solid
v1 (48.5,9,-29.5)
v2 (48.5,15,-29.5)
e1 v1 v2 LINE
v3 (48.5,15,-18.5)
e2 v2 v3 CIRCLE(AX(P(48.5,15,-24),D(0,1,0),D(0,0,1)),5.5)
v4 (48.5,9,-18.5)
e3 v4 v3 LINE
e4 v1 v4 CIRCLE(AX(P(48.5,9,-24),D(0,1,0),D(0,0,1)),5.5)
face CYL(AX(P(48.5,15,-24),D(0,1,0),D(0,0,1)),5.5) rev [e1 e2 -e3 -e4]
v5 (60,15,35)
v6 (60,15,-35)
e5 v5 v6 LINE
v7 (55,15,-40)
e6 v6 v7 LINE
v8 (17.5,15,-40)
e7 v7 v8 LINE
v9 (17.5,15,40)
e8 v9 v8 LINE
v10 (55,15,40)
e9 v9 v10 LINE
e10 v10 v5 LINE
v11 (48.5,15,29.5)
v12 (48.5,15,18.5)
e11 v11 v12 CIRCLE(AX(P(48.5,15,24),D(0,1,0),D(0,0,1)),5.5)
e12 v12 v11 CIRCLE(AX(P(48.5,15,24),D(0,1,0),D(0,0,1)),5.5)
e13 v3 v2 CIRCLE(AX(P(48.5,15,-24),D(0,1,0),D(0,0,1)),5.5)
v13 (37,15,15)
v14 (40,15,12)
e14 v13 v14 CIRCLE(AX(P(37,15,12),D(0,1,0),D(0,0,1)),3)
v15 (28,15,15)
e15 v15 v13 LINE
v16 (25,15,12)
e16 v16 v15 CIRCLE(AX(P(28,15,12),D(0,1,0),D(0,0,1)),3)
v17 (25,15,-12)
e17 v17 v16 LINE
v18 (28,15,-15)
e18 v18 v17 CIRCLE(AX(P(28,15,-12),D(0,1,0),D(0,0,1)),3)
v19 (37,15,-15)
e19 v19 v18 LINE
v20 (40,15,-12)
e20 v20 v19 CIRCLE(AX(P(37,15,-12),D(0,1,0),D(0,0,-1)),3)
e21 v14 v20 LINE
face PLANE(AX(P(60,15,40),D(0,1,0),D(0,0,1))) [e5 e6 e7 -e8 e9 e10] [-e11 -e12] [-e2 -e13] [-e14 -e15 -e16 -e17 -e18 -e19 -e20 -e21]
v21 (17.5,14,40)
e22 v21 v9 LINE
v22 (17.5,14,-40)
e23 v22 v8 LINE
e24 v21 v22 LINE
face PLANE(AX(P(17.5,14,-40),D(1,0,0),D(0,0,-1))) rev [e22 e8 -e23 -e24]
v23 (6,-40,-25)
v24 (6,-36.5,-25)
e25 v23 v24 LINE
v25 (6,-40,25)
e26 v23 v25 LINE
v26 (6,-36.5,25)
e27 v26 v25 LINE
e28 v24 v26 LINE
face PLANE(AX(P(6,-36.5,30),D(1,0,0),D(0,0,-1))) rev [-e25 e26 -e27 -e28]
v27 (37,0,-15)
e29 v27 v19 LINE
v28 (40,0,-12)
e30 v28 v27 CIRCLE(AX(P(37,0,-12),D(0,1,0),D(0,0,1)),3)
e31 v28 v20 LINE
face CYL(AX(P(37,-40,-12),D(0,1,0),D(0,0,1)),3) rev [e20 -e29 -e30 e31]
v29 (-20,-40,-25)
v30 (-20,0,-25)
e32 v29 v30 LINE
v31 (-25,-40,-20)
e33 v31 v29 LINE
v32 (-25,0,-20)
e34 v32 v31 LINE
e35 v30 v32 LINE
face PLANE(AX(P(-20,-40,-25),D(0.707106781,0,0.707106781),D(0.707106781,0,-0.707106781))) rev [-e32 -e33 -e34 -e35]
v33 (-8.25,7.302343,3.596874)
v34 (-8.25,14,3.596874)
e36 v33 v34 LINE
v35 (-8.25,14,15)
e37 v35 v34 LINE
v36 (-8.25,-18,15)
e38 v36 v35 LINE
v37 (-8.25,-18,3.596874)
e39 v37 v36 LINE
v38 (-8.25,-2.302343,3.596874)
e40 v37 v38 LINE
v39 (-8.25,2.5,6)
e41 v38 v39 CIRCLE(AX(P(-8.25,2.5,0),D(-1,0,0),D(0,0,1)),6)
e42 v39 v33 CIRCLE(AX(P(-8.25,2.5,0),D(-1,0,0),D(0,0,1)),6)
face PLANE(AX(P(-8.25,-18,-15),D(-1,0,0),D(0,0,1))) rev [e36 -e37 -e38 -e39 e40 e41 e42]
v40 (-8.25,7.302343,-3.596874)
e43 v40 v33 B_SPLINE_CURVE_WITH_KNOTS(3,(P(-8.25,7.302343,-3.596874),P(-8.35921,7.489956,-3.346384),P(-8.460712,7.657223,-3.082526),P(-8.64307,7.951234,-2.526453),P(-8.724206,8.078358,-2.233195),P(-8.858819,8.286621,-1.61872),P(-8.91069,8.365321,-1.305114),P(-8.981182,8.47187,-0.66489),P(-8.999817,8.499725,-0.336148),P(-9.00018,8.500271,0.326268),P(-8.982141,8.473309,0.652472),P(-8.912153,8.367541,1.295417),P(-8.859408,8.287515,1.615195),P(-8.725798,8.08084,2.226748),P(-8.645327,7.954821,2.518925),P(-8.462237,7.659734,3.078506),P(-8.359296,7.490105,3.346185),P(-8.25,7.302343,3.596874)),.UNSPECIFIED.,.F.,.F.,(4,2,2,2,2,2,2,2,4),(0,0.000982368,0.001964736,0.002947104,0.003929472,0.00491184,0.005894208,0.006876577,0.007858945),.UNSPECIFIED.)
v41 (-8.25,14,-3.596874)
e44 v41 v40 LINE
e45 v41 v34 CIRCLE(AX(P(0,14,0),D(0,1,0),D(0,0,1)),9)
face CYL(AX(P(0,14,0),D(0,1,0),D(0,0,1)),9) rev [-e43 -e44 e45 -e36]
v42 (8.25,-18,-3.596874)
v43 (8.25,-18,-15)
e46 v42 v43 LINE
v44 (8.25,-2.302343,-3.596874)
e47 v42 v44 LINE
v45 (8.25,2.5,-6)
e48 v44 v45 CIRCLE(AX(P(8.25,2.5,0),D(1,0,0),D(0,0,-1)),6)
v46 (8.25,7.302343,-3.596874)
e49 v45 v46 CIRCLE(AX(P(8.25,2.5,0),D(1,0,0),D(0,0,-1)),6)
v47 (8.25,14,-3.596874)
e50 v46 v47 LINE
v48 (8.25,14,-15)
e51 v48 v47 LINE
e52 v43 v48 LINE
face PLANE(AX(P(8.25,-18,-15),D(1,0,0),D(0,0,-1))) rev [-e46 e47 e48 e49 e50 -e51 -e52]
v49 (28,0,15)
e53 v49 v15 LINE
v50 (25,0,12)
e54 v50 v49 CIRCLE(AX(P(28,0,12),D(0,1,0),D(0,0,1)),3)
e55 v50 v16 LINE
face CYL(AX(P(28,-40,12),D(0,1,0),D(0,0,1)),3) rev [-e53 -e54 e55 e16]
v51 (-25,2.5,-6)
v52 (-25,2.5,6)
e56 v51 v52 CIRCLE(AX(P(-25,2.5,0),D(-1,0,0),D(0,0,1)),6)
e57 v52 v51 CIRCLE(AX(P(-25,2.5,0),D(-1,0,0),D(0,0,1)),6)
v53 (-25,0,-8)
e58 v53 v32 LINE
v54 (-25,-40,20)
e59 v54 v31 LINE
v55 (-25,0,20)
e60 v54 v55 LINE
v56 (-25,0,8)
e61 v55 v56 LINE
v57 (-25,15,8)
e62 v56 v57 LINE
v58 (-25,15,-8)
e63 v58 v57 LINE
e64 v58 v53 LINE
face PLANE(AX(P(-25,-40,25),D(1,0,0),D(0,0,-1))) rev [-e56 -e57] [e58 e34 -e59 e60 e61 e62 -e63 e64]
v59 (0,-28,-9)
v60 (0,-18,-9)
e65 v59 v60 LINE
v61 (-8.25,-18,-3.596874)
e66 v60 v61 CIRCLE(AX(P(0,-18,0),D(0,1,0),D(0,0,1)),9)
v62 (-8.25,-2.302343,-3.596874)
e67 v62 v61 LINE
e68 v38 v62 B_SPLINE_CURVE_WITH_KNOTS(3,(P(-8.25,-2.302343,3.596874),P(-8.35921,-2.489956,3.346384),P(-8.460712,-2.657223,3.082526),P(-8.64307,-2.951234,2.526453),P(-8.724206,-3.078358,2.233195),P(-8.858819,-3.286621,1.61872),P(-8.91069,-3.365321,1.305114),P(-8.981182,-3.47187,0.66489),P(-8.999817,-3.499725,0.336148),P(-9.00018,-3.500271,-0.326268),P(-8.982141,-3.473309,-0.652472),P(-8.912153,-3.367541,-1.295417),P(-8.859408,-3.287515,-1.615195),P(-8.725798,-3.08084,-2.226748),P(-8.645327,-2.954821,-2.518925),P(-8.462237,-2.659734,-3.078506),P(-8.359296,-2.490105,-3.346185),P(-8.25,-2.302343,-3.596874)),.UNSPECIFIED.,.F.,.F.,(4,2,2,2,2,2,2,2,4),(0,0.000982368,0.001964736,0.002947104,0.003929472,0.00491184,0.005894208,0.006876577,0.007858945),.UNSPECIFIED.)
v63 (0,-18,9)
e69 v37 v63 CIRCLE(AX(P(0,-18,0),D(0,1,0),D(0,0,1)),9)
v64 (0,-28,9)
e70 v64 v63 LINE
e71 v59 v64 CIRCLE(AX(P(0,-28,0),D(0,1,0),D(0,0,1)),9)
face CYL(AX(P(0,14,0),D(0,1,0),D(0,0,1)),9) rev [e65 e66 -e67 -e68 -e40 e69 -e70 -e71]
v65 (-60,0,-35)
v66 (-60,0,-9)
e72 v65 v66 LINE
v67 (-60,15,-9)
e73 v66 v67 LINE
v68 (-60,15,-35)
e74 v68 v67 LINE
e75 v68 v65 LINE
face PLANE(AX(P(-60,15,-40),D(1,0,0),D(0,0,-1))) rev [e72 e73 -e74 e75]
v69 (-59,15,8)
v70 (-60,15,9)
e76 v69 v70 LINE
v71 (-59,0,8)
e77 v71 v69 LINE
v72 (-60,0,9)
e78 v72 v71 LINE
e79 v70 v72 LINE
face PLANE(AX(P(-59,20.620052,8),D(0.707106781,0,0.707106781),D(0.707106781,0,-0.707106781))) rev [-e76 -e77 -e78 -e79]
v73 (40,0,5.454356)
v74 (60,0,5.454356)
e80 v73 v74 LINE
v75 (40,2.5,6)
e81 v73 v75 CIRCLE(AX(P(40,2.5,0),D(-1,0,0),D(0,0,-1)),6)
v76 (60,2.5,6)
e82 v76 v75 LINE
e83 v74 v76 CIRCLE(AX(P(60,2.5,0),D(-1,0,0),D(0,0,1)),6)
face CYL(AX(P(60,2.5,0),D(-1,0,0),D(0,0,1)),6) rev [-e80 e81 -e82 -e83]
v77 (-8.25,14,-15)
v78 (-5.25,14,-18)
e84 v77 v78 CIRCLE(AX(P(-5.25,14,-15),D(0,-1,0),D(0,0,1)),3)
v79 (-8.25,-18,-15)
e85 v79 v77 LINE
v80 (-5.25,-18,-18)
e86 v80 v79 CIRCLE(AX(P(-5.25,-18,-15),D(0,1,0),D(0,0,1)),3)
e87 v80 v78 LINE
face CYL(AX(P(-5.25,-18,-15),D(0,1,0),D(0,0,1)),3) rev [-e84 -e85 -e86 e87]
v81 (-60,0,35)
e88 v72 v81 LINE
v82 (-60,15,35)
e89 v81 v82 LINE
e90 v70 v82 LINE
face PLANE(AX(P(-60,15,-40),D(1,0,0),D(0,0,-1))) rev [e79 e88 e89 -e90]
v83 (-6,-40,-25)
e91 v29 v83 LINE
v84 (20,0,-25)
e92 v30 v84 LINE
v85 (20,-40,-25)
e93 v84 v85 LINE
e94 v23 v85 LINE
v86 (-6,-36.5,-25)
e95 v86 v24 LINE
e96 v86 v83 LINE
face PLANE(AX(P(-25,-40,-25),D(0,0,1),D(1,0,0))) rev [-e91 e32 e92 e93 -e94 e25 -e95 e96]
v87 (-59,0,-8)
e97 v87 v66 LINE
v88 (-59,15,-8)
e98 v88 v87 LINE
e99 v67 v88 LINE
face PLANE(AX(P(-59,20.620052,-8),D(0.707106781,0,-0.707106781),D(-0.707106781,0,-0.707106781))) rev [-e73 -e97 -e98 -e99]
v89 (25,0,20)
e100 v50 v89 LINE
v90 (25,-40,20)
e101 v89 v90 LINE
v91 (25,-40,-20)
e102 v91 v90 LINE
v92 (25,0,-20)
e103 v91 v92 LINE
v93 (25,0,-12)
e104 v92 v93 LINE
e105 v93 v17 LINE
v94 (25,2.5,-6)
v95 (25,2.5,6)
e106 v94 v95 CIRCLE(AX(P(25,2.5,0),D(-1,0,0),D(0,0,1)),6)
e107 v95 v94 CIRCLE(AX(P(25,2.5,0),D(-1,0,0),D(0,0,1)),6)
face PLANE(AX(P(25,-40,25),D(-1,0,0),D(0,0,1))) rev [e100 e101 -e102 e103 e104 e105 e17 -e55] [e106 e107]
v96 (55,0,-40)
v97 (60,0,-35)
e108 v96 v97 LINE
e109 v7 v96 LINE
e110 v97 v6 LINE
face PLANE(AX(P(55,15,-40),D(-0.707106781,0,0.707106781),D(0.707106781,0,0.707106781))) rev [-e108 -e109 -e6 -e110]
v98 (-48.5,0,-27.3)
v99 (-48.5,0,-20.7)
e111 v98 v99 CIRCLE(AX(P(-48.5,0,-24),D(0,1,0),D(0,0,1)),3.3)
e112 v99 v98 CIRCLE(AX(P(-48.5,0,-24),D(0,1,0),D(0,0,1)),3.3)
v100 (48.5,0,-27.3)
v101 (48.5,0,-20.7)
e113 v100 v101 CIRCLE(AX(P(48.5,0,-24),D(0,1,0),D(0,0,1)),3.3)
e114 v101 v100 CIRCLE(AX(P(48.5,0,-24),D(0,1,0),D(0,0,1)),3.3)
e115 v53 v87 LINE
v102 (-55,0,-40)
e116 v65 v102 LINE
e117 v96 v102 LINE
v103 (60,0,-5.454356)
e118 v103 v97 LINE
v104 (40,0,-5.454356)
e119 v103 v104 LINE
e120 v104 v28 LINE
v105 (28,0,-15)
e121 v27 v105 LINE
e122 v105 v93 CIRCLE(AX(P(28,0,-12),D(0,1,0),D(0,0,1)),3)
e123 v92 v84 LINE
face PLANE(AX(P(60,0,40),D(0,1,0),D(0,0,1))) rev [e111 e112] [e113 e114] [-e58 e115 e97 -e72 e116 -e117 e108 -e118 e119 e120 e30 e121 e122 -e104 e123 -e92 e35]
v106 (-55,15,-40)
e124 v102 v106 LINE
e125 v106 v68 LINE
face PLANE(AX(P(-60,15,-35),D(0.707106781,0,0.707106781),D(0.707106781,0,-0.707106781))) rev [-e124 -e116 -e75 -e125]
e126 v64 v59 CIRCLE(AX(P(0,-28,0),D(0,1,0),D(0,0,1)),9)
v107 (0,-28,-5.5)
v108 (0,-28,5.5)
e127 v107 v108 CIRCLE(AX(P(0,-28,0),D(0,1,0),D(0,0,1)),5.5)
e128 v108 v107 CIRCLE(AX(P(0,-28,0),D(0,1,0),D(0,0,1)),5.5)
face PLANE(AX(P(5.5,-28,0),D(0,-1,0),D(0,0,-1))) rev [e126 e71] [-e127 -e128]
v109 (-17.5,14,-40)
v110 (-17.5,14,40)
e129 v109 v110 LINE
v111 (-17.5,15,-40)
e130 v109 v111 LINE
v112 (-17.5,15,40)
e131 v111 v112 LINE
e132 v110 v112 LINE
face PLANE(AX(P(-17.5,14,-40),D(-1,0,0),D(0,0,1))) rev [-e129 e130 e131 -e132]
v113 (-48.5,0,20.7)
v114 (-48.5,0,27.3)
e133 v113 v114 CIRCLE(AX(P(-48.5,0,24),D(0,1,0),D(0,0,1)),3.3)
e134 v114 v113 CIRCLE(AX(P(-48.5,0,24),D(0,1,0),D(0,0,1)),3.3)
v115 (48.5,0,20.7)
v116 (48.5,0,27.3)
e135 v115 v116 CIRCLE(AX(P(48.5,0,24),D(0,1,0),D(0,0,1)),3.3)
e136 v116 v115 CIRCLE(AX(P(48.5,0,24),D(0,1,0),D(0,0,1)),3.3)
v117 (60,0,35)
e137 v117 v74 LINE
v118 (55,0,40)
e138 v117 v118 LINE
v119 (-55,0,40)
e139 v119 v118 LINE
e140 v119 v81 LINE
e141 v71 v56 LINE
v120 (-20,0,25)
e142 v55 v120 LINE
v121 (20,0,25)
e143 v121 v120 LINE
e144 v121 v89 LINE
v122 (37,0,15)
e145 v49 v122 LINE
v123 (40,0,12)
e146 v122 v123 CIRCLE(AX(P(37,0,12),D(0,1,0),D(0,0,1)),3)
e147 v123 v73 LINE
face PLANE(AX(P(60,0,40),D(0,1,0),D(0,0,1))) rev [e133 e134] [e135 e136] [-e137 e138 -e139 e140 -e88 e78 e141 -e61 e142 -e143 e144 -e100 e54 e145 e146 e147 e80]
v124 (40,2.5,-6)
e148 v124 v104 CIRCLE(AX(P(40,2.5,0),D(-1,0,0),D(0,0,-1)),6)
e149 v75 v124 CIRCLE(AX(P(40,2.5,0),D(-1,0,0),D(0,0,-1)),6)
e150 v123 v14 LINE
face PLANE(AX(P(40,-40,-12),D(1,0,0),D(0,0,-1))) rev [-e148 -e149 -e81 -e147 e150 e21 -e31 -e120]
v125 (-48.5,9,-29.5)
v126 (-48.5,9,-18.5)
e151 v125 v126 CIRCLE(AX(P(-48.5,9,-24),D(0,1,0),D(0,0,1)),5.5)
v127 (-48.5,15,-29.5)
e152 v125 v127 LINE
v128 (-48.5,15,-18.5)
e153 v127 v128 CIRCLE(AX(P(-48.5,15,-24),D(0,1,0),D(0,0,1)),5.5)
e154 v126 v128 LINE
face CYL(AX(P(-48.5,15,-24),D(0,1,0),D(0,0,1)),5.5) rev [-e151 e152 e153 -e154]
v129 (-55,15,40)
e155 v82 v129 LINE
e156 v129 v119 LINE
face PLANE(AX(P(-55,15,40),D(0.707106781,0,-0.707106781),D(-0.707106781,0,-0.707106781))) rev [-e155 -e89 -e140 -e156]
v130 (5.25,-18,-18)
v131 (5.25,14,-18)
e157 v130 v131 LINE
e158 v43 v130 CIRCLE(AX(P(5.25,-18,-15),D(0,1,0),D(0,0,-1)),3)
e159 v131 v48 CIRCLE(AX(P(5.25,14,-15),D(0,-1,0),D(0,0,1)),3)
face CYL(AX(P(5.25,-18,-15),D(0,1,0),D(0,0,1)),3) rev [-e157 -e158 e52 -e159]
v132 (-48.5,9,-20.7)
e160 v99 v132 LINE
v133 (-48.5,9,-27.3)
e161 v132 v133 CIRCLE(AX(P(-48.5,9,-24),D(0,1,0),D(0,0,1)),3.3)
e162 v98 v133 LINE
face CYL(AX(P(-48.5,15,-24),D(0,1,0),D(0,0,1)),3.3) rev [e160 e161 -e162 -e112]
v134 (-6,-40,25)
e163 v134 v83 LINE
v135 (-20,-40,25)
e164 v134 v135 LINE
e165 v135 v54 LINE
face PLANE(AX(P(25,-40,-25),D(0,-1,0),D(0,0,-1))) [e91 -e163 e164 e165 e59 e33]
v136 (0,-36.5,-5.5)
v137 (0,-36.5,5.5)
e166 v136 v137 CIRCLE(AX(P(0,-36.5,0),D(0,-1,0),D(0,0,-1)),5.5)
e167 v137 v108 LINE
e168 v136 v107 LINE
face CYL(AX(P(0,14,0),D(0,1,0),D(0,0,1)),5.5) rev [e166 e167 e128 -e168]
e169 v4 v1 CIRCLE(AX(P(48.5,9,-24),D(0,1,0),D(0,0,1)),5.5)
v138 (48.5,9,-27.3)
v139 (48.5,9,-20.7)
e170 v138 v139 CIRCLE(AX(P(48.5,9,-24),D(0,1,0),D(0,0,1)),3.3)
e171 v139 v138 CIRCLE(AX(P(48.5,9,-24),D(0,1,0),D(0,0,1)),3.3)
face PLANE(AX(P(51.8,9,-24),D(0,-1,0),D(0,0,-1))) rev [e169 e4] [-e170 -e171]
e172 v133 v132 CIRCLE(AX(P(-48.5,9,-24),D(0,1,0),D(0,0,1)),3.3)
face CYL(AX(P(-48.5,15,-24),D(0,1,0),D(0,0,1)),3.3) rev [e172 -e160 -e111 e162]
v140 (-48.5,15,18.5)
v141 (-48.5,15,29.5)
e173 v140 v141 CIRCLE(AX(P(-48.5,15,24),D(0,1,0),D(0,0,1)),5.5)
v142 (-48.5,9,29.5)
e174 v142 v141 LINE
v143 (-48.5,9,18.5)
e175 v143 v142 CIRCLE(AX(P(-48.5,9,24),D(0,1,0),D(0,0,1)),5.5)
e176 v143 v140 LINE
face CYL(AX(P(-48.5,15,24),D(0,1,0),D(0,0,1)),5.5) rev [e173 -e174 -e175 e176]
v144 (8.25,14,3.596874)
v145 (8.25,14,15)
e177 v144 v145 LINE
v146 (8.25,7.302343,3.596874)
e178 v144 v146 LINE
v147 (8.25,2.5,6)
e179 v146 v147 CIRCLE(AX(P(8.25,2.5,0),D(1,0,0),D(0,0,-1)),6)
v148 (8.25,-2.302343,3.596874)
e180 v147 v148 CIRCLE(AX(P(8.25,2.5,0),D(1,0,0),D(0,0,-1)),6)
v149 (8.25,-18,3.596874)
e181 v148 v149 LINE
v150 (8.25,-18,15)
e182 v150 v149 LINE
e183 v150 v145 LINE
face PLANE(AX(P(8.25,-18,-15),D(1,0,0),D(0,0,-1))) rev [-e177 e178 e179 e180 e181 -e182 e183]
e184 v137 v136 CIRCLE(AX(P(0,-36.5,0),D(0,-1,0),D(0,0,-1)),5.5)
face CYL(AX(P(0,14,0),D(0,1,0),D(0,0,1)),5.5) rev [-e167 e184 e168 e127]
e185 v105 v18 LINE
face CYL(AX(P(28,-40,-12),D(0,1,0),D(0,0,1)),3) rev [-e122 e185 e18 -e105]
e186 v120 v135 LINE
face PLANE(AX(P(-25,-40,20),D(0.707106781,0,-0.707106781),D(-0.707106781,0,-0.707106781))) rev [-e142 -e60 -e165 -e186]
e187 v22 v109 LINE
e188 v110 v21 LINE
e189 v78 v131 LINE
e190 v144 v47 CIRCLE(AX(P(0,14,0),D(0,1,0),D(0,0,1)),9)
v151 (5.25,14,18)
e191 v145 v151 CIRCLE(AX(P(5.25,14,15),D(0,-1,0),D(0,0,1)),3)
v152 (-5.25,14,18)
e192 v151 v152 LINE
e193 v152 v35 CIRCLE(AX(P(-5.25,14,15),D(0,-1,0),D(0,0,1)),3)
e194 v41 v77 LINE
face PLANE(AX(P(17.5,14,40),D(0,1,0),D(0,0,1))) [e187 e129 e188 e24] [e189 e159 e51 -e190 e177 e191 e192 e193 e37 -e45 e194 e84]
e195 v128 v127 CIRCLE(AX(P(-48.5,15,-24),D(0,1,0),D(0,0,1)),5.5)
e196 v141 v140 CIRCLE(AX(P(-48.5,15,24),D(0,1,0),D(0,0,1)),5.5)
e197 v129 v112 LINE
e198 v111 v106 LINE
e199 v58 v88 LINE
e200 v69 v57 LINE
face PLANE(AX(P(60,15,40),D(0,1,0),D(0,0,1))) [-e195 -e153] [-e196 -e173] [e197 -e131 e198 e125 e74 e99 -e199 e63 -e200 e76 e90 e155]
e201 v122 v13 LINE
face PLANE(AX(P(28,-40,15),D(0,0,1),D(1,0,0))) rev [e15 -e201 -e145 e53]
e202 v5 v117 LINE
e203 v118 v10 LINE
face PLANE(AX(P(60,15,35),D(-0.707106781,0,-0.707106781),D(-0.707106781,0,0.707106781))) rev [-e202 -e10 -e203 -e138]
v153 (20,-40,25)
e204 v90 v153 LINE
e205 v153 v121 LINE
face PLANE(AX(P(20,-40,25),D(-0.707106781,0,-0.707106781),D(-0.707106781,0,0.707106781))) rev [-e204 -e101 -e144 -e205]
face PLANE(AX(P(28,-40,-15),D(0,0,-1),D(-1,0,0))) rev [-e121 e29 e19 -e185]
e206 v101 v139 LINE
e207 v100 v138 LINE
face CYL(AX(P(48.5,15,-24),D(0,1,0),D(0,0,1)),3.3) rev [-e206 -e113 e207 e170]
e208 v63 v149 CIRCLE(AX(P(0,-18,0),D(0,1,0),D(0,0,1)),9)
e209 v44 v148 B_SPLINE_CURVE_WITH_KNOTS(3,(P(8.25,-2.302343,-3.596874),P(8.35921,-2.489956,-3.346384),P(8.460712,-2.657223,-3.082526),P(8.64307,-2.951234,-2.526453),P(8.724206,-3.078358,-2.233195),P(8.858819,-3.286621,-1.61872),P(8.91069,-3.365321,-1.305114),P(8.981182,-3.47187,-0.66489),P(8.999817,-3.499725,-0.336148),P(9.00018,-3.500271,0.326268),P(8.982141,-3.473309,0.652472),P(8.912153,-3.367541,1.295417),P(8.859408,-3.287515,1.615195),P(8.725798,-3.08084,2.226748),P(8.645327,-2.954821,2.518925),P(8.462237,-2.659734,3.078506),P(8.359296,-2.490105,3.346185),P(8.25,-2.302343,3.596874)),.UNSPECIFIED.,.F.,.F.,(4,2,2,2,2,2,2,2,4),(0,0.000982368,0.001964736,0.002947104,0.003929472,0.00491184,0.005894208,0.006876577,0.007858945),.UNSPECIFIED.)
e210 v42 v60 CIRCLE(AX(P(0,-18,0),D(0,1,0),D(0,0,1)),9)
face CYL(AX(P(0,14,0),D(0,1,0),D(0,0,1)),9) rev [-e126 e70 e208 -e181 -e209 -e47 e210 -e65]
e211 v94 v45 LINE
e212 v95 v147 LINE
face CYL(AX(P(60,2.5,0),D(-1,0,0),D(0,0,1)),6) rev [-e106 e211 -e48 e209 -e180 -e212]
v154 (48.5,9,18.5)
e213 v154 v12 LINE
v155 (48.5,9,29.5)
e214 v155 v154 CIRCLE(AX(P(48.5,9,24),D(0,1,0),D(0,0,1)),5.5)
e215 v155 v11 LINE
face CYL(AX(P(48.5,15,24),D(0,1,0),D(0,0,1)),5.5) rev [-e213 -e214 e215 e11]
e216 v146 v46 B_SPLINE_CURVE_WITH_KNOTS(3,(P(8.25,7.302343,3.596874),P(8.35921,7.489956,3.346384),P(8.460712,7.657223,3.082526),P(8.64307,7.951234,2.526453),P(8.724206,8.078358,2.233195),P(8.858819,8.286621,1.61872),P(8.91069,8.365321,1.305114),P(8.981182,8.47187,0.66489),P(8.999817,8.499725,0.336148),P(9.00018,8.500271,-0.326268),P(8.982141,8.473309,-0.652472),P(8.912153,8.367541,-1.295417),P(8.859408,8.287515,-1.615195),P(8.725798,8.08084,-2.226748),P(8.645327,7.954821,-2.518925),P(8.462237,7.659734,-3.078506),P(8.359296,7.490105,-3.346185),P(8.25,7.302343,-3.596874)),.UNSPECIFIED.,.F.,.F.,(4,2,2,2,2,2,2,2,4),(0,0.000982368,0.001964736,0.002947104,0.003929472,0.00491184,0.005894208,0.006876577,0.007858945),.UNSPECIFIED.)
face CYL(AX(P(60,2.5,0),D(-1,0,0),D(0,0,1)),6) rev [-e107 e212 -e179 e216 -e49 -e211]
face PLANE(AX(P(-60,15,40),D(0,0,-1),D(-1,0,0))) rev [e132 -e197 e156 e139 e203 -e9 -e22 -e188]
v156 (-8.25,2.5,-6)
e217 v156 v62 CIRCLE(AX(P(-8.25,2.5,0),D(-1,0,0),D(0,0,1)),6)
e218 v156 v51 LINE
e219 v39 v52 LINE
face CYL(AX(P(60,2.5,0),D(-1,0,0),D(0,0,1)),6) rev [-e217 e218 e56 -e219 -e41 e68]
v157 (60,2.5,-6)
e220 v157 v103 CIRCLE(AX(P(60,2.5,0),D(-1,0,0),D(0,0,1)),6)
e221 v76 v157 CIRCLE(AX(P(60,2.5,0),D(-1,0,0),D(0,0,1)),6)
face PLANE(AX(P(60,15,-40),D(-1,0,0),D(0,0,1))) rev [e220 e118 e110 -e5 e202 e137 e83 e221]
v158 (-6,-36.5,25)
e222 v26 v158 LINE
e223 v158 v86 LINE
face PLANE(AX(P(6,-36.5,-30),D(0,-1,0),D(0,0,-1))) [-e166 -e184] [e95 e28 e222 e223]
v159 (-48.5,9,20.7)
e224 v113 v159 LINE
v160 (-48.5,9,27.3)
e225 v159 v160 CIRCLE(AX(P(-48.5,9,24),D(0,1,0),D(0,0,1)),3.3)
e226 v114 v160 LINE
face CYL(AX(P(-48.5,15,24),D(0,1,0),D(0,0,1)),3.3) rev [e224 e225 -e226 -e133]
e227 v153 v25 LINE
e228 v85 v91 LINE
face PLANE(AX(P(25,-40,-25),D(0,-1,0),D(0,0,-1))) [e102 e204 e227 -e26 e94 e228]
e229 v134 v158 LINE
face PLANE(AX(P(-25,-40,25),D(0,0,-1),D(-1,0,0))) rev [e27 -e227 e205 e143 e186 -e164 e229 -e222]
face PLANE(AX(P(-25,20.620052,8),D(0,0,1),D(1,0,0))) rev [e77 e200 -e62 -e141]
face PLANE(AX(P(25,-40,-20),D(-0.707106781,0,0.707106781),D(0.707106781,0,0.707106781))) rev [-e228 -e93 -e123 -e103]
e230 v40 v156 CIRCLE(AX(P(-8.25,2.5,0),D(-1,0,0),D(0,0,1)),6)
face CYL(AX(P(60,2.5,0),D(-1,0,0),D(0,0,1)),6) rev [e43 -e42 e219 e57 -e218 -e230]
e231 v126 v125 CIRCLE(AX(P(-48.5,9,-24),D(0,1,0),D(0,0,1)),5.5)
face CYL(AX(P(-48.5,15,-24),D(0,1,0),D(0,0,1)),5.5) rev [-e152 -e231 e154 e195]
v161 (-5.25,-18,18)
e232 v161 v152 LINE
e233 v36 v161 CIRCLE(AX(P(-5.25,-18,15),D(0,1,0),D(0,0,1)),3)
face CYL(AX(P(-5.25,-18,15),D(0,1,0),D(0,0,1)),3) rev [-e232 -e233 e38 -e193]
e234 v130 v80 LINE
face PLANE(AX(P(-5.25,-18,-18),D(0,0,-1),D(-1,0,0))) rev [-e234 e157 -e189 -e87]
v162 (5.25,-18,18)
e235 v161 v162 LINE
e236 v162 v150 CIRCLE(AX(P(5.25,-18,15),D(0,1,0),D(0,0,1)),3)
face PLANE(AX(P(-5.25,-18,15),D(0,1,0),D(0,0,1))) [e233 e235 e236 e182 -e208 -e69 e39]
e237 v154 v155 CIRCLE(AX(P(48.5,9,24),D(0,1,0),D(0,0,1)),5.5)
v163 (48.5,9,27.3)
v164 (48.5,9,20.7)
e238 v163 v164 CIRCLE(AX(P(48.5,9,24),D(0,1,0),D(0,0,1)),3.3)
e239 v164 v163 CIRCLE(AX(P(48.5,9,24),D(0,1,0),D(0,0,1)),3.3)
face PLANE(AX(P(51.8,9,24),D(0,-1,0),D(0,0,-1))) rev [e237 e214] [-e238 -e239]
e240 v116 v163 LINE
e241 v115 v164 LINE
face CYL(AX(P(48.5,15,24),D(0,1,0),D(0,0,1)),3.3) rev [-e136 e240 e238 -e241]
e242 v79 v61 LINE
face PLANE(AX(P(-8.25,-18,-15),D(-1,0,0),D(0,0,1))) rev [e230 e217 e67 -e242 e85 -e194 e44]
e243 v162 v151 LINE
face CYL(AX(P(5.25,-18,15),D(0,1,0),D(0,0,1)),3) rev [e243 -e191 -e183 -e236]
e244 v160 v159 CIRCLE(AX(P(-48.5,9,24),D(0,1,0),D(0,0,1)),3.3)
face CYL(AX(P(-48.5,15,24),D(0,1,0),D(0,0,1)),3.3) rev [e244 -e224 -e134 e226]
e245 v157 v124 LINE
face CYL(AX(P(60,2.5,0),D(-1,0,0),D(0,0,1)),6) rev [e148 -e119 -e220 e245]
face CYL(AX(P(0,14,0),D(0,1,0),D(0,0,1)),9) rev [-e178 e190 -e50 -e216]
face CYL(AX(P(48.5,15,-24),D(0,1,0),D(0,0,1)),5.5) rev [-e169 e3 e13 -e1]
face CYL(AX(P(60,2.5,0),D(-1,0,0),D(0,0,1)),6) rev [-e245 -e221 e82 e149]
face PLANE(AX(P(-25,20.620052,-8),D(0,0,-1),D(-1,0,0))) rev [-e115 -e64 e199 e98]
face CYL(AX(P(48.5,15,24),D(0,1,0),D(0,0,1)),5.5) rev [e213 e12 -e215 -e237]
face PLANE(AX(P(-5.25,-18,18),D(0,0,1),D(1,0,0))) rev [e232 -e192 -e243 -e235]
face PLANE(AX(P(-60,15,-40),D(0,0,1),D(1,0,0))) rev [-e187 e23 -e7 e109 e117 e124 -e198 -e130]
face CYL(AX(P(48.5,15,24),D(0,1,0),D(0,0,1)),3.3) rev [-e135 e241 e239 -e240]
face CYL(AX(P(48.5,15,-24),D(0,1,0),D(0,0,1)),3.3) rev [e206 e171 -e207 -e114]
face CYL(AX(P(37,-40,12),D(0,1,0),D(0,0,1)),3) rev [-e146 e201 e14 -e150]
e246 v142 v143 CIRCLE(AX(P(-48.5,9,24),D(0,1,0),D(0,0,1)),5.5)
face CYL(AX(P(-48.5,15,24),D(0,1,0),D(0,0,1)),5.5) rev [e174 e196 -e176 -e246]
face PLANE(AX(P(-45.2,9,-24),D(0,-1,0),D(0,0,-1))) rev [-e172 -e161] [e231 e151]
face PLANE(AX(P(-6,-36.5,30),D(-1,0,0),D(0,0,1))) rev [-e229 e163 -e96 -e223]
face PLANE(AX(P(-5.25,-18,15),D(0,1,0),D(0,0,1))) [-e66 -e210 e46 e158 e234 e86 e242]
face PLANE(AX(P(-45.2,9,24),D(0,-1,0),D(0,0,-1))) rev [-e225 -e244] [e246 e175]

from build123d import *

# Parameters (mm, degrees)
SKETCH1_W                                            = 120
SKETCH1_H                                            = 80
BOSS_EXTRUDE1_DEPTH                                  = 15
SKETCH2_W                                            = 50
SKETCH2_H                                            = 50
BOSS_EXTRUDE2_DEPTH                                  = 40
CUT_EXTRUDE2_DEPTH                                   = 33
SKETCH5_W                                            = 16
SKETCH5_H                                            = 41.240104646
CUT_EXTRUDE3_DEPTH                                   = 35
SKETCH6_R                                            = 6
CUT_EXTRUDE4_DEPTH                                   = 103.102889283
CBORE_FOR_M6_HEX_SOCKET_HEAD_CAP_SCREW1_D            = 6.6
CBORE_FOR_M6_HEX_SOCKET_HEAD_CAP_SCREW1_CBORE_D      = 11
CBORE_FOR_M6_HEX_SOCKET_HEAD_CAP_SCREW1_CBORE_DEPTH  = 6
SKETCH11_W                                           = 12
SKETCH11_H                                           = 60
CUT_EXTRUDE5_DEPTH                                   = 3.5
CUT_EXTRUDE7_DEPTH                                   = 91.691785736
CHAMFER1_SIZE                                        = 5
CHAMFER2_SIZE                                        = 1
SKETCH14_W                                           = 35
SKETCH14_H                                           = 80
CUT_EXTRUDE8_DEPTH                                   = 1
CBORE_FOR_M10_HEX_SOCKET_HEAD_CAP_SCREW1_D           = 11
CBORE_FOR_M10_HEX_SOCKET_HEAD_CAP_SCREW1_CBORE_D     = 18
CBORE_FOR_M10_HEX_SOCKET_HEAD_CAP_SCREW1_CBORE_DEPTH = 42


with BuildPart() as part:
    # Sketch1 → Boss-Extrude1 (new body)
    with BuildSketch(Plane(origin=(0, 0, 0), x_dir=(1, 0, 0), z_dir=(0, 1, 0))):
        Rectangle(SKETCH1_W, SKETCH1_H)
    extrude(amount=BOSS_EXTRUDE1_DEPTH)

    # Sketch2 → Boss-Extrude2 (add)
    with BuildSketch(Plane.XZ):
        Rectangle(SKETCH2_W, SKETCH2_H)
    extrude(amount=BOSS_EXTRUDE2_DEPTH)

    # Sketch4 → Cut-Extrude2 (cut)
    with BuildSketch(Plane(origin=(0, 15, 0), x_dir=(1, 0, 0), z_dir=(0, 1, 0))):
        with BuildLine():
            Line((-5.25, 18), (5.25, 18))
            ThreePointArc((5.25, 18), (7.371320344, 17.121320344), (8.25, 15))
            Line((8.25, 15), (8.25, -15))
            ThreePointArc((8.25, -15), (7.371320344, -17.121320344), (5.25, -18))
            Line((5.25, -18), (-5.25, -18))
            ThreePointArc((-5.25, -18), (-7.371320344, -17.121320344), (-8.25, -15))
            Line((-8.25, -15), (-8.25, 15))
            ThreePointArc((-8.25, 15), (-7.371320344, 17.121320344), (-5.25, 18))
        make_face()
    extrude(amount=-CUT_EXTRUDE2_DEPTH, mode=Mode.SUBTRACT)

    # Sketch5 → Cut-Extrude3 (cut)
    with BuildSketch(Plane.ZY.offset(60)):
        Rectangle(SKETCH5_W, SKETCH5_H)
    extrude(amount=-CUT_EXTRUDE3_DEPTH, mode=Mode.SUBTRACT)

    # Sketch6 → Cut-Extrude4 (cut, through all)
    with BuildSketch(Plane.ZY.offset(25)):
        with Locations(Location((0, 2.5, 0), (0, 0, 335.375681648))):
            Circle(SKETCH6_R)
    extrude(amount=-CUT_EXTRUDE4_DEPTH, mode=Mode.SUBTRACT)

    # CBORE for M6 Hex Socket Head Cap Screw1 (through all)
    with Locations(Plane(origin=(0, 15, 0), x_dir=(-1, 0, 0), z_dir=(0, 1, 0))):
        with Locations((48.5, 24), (-48.5, 24), (-48.5, -24), (48.5, -24)):
            CounterBoreHole(CBORE_FOR_M6_HEX_SOCKET_HEAD_CAP_SCREW1_D / 2, CBORE_FOR_M6_HEX_SOCKET_HEAD_CAP_SCREW1_CBORE_D / 2, CBORE_FOR_M6_HEX_SOCKET_HEAD_CAP_SCREW1_CBORE_DEPTH)

    # Sketch11 → Cut-Extrude5 (cut)
    with BuildSketch(Plane.XZ.offset(40)):
        Rectangle(SKETCH11_W, SKETCH11_H)
    extrude(amount=-CUT_EXTRUDE5_DEPTH, mode=Mode.SUBTRACT)

    # Sketch13 → Cut-Extrude7 (cut, through all)
    with BuildSketch(Plane(origin=(0, 15, 0), x_dir=(1, 0, 0), z_dir=(0, 1, 0))):
        with BuildLine():
            Line((28, 15), (37, 15))
            ThreePointArc((37, 15), (39.121320344, 14.121320344), (40, 12))
            Line((40, 12), (40, -12))
            ThreePointArc((40, -12), (39.121320344, -14.121320344), (37, -15))
            Line((37, -15), (28, -15))
            ThreePointArc((28, -15), (25.878679656, -14.121320344), (25, -12))
            Line((25, -12), (25, 12))
            ThreePointArc((25, 12), (25.878679656, 14.121320344), (28, 15))
        make_face()
    extrude(amount=-CUT_EXTRUDE7_DEPTH, mode=Mode.SUBTRACT)

    # Chamfer1
    chamfer1_edges = [part.edges().sort_by_distance(p)[0] for p in [
        (25, -20, -25),
        (25, -20, 25),
        (-25, -20, 25),
        (-25, -20, -25),
        (60, 7.5, 40),
        (-60, 7.5, 40),
        (-60, 7.5, -40),
        (60, 7.5, -40),
    ]]
    chamfer(chamfer1_edges, length=CHAMFER1_SIZE)

    # Chamfer2
    chamfer2_edges = [part.edges().sort_by_distance(p)[0] for p in [
        (-60, 7.5, -8),
        (-60, 7.5, 8),
    ]]
    chamfer(chamfer2_edges, length=CHAMFER2_SIZE)

    # Sketch14 → Cut-Extrude8 (cut)
    with BuildSketch(Plane(origin=(0, 15, 0), x_dir=(1, 0, 0), z_dir=(0, 1, 0))):
        Rectangle(SKETCH14_W, SKETCH14_H)
    extrude(amount=-CUT_EXTRUDE8_DEPTH, mode=Mode.SUBTRACT)

    # CBORE for M10 Hex Socket Head Cap Screw1 (through all)
    with Locations(Plane(origin=(-12.636834377, 14, 0.883421015), x_dir=(-1, 0, 0), z_dir=(0, 1, 0))):
        with Locations((-12.636834377, -0.883421015)):
            CounterBoreHole(CBORE_FOR_M10_HEX_SOCKET_HEAD_CAP_SCREW1_D / 2, CBORE_FOR_M10_HEX_SOCKET_HEAD_CAP_SCREW1_CBORE_D / 2, CBORE_FOR_M10_HEX_SOCKET_HEAD_CAP_SCREW1_CBORE_DEPTH)


solid = part.part
